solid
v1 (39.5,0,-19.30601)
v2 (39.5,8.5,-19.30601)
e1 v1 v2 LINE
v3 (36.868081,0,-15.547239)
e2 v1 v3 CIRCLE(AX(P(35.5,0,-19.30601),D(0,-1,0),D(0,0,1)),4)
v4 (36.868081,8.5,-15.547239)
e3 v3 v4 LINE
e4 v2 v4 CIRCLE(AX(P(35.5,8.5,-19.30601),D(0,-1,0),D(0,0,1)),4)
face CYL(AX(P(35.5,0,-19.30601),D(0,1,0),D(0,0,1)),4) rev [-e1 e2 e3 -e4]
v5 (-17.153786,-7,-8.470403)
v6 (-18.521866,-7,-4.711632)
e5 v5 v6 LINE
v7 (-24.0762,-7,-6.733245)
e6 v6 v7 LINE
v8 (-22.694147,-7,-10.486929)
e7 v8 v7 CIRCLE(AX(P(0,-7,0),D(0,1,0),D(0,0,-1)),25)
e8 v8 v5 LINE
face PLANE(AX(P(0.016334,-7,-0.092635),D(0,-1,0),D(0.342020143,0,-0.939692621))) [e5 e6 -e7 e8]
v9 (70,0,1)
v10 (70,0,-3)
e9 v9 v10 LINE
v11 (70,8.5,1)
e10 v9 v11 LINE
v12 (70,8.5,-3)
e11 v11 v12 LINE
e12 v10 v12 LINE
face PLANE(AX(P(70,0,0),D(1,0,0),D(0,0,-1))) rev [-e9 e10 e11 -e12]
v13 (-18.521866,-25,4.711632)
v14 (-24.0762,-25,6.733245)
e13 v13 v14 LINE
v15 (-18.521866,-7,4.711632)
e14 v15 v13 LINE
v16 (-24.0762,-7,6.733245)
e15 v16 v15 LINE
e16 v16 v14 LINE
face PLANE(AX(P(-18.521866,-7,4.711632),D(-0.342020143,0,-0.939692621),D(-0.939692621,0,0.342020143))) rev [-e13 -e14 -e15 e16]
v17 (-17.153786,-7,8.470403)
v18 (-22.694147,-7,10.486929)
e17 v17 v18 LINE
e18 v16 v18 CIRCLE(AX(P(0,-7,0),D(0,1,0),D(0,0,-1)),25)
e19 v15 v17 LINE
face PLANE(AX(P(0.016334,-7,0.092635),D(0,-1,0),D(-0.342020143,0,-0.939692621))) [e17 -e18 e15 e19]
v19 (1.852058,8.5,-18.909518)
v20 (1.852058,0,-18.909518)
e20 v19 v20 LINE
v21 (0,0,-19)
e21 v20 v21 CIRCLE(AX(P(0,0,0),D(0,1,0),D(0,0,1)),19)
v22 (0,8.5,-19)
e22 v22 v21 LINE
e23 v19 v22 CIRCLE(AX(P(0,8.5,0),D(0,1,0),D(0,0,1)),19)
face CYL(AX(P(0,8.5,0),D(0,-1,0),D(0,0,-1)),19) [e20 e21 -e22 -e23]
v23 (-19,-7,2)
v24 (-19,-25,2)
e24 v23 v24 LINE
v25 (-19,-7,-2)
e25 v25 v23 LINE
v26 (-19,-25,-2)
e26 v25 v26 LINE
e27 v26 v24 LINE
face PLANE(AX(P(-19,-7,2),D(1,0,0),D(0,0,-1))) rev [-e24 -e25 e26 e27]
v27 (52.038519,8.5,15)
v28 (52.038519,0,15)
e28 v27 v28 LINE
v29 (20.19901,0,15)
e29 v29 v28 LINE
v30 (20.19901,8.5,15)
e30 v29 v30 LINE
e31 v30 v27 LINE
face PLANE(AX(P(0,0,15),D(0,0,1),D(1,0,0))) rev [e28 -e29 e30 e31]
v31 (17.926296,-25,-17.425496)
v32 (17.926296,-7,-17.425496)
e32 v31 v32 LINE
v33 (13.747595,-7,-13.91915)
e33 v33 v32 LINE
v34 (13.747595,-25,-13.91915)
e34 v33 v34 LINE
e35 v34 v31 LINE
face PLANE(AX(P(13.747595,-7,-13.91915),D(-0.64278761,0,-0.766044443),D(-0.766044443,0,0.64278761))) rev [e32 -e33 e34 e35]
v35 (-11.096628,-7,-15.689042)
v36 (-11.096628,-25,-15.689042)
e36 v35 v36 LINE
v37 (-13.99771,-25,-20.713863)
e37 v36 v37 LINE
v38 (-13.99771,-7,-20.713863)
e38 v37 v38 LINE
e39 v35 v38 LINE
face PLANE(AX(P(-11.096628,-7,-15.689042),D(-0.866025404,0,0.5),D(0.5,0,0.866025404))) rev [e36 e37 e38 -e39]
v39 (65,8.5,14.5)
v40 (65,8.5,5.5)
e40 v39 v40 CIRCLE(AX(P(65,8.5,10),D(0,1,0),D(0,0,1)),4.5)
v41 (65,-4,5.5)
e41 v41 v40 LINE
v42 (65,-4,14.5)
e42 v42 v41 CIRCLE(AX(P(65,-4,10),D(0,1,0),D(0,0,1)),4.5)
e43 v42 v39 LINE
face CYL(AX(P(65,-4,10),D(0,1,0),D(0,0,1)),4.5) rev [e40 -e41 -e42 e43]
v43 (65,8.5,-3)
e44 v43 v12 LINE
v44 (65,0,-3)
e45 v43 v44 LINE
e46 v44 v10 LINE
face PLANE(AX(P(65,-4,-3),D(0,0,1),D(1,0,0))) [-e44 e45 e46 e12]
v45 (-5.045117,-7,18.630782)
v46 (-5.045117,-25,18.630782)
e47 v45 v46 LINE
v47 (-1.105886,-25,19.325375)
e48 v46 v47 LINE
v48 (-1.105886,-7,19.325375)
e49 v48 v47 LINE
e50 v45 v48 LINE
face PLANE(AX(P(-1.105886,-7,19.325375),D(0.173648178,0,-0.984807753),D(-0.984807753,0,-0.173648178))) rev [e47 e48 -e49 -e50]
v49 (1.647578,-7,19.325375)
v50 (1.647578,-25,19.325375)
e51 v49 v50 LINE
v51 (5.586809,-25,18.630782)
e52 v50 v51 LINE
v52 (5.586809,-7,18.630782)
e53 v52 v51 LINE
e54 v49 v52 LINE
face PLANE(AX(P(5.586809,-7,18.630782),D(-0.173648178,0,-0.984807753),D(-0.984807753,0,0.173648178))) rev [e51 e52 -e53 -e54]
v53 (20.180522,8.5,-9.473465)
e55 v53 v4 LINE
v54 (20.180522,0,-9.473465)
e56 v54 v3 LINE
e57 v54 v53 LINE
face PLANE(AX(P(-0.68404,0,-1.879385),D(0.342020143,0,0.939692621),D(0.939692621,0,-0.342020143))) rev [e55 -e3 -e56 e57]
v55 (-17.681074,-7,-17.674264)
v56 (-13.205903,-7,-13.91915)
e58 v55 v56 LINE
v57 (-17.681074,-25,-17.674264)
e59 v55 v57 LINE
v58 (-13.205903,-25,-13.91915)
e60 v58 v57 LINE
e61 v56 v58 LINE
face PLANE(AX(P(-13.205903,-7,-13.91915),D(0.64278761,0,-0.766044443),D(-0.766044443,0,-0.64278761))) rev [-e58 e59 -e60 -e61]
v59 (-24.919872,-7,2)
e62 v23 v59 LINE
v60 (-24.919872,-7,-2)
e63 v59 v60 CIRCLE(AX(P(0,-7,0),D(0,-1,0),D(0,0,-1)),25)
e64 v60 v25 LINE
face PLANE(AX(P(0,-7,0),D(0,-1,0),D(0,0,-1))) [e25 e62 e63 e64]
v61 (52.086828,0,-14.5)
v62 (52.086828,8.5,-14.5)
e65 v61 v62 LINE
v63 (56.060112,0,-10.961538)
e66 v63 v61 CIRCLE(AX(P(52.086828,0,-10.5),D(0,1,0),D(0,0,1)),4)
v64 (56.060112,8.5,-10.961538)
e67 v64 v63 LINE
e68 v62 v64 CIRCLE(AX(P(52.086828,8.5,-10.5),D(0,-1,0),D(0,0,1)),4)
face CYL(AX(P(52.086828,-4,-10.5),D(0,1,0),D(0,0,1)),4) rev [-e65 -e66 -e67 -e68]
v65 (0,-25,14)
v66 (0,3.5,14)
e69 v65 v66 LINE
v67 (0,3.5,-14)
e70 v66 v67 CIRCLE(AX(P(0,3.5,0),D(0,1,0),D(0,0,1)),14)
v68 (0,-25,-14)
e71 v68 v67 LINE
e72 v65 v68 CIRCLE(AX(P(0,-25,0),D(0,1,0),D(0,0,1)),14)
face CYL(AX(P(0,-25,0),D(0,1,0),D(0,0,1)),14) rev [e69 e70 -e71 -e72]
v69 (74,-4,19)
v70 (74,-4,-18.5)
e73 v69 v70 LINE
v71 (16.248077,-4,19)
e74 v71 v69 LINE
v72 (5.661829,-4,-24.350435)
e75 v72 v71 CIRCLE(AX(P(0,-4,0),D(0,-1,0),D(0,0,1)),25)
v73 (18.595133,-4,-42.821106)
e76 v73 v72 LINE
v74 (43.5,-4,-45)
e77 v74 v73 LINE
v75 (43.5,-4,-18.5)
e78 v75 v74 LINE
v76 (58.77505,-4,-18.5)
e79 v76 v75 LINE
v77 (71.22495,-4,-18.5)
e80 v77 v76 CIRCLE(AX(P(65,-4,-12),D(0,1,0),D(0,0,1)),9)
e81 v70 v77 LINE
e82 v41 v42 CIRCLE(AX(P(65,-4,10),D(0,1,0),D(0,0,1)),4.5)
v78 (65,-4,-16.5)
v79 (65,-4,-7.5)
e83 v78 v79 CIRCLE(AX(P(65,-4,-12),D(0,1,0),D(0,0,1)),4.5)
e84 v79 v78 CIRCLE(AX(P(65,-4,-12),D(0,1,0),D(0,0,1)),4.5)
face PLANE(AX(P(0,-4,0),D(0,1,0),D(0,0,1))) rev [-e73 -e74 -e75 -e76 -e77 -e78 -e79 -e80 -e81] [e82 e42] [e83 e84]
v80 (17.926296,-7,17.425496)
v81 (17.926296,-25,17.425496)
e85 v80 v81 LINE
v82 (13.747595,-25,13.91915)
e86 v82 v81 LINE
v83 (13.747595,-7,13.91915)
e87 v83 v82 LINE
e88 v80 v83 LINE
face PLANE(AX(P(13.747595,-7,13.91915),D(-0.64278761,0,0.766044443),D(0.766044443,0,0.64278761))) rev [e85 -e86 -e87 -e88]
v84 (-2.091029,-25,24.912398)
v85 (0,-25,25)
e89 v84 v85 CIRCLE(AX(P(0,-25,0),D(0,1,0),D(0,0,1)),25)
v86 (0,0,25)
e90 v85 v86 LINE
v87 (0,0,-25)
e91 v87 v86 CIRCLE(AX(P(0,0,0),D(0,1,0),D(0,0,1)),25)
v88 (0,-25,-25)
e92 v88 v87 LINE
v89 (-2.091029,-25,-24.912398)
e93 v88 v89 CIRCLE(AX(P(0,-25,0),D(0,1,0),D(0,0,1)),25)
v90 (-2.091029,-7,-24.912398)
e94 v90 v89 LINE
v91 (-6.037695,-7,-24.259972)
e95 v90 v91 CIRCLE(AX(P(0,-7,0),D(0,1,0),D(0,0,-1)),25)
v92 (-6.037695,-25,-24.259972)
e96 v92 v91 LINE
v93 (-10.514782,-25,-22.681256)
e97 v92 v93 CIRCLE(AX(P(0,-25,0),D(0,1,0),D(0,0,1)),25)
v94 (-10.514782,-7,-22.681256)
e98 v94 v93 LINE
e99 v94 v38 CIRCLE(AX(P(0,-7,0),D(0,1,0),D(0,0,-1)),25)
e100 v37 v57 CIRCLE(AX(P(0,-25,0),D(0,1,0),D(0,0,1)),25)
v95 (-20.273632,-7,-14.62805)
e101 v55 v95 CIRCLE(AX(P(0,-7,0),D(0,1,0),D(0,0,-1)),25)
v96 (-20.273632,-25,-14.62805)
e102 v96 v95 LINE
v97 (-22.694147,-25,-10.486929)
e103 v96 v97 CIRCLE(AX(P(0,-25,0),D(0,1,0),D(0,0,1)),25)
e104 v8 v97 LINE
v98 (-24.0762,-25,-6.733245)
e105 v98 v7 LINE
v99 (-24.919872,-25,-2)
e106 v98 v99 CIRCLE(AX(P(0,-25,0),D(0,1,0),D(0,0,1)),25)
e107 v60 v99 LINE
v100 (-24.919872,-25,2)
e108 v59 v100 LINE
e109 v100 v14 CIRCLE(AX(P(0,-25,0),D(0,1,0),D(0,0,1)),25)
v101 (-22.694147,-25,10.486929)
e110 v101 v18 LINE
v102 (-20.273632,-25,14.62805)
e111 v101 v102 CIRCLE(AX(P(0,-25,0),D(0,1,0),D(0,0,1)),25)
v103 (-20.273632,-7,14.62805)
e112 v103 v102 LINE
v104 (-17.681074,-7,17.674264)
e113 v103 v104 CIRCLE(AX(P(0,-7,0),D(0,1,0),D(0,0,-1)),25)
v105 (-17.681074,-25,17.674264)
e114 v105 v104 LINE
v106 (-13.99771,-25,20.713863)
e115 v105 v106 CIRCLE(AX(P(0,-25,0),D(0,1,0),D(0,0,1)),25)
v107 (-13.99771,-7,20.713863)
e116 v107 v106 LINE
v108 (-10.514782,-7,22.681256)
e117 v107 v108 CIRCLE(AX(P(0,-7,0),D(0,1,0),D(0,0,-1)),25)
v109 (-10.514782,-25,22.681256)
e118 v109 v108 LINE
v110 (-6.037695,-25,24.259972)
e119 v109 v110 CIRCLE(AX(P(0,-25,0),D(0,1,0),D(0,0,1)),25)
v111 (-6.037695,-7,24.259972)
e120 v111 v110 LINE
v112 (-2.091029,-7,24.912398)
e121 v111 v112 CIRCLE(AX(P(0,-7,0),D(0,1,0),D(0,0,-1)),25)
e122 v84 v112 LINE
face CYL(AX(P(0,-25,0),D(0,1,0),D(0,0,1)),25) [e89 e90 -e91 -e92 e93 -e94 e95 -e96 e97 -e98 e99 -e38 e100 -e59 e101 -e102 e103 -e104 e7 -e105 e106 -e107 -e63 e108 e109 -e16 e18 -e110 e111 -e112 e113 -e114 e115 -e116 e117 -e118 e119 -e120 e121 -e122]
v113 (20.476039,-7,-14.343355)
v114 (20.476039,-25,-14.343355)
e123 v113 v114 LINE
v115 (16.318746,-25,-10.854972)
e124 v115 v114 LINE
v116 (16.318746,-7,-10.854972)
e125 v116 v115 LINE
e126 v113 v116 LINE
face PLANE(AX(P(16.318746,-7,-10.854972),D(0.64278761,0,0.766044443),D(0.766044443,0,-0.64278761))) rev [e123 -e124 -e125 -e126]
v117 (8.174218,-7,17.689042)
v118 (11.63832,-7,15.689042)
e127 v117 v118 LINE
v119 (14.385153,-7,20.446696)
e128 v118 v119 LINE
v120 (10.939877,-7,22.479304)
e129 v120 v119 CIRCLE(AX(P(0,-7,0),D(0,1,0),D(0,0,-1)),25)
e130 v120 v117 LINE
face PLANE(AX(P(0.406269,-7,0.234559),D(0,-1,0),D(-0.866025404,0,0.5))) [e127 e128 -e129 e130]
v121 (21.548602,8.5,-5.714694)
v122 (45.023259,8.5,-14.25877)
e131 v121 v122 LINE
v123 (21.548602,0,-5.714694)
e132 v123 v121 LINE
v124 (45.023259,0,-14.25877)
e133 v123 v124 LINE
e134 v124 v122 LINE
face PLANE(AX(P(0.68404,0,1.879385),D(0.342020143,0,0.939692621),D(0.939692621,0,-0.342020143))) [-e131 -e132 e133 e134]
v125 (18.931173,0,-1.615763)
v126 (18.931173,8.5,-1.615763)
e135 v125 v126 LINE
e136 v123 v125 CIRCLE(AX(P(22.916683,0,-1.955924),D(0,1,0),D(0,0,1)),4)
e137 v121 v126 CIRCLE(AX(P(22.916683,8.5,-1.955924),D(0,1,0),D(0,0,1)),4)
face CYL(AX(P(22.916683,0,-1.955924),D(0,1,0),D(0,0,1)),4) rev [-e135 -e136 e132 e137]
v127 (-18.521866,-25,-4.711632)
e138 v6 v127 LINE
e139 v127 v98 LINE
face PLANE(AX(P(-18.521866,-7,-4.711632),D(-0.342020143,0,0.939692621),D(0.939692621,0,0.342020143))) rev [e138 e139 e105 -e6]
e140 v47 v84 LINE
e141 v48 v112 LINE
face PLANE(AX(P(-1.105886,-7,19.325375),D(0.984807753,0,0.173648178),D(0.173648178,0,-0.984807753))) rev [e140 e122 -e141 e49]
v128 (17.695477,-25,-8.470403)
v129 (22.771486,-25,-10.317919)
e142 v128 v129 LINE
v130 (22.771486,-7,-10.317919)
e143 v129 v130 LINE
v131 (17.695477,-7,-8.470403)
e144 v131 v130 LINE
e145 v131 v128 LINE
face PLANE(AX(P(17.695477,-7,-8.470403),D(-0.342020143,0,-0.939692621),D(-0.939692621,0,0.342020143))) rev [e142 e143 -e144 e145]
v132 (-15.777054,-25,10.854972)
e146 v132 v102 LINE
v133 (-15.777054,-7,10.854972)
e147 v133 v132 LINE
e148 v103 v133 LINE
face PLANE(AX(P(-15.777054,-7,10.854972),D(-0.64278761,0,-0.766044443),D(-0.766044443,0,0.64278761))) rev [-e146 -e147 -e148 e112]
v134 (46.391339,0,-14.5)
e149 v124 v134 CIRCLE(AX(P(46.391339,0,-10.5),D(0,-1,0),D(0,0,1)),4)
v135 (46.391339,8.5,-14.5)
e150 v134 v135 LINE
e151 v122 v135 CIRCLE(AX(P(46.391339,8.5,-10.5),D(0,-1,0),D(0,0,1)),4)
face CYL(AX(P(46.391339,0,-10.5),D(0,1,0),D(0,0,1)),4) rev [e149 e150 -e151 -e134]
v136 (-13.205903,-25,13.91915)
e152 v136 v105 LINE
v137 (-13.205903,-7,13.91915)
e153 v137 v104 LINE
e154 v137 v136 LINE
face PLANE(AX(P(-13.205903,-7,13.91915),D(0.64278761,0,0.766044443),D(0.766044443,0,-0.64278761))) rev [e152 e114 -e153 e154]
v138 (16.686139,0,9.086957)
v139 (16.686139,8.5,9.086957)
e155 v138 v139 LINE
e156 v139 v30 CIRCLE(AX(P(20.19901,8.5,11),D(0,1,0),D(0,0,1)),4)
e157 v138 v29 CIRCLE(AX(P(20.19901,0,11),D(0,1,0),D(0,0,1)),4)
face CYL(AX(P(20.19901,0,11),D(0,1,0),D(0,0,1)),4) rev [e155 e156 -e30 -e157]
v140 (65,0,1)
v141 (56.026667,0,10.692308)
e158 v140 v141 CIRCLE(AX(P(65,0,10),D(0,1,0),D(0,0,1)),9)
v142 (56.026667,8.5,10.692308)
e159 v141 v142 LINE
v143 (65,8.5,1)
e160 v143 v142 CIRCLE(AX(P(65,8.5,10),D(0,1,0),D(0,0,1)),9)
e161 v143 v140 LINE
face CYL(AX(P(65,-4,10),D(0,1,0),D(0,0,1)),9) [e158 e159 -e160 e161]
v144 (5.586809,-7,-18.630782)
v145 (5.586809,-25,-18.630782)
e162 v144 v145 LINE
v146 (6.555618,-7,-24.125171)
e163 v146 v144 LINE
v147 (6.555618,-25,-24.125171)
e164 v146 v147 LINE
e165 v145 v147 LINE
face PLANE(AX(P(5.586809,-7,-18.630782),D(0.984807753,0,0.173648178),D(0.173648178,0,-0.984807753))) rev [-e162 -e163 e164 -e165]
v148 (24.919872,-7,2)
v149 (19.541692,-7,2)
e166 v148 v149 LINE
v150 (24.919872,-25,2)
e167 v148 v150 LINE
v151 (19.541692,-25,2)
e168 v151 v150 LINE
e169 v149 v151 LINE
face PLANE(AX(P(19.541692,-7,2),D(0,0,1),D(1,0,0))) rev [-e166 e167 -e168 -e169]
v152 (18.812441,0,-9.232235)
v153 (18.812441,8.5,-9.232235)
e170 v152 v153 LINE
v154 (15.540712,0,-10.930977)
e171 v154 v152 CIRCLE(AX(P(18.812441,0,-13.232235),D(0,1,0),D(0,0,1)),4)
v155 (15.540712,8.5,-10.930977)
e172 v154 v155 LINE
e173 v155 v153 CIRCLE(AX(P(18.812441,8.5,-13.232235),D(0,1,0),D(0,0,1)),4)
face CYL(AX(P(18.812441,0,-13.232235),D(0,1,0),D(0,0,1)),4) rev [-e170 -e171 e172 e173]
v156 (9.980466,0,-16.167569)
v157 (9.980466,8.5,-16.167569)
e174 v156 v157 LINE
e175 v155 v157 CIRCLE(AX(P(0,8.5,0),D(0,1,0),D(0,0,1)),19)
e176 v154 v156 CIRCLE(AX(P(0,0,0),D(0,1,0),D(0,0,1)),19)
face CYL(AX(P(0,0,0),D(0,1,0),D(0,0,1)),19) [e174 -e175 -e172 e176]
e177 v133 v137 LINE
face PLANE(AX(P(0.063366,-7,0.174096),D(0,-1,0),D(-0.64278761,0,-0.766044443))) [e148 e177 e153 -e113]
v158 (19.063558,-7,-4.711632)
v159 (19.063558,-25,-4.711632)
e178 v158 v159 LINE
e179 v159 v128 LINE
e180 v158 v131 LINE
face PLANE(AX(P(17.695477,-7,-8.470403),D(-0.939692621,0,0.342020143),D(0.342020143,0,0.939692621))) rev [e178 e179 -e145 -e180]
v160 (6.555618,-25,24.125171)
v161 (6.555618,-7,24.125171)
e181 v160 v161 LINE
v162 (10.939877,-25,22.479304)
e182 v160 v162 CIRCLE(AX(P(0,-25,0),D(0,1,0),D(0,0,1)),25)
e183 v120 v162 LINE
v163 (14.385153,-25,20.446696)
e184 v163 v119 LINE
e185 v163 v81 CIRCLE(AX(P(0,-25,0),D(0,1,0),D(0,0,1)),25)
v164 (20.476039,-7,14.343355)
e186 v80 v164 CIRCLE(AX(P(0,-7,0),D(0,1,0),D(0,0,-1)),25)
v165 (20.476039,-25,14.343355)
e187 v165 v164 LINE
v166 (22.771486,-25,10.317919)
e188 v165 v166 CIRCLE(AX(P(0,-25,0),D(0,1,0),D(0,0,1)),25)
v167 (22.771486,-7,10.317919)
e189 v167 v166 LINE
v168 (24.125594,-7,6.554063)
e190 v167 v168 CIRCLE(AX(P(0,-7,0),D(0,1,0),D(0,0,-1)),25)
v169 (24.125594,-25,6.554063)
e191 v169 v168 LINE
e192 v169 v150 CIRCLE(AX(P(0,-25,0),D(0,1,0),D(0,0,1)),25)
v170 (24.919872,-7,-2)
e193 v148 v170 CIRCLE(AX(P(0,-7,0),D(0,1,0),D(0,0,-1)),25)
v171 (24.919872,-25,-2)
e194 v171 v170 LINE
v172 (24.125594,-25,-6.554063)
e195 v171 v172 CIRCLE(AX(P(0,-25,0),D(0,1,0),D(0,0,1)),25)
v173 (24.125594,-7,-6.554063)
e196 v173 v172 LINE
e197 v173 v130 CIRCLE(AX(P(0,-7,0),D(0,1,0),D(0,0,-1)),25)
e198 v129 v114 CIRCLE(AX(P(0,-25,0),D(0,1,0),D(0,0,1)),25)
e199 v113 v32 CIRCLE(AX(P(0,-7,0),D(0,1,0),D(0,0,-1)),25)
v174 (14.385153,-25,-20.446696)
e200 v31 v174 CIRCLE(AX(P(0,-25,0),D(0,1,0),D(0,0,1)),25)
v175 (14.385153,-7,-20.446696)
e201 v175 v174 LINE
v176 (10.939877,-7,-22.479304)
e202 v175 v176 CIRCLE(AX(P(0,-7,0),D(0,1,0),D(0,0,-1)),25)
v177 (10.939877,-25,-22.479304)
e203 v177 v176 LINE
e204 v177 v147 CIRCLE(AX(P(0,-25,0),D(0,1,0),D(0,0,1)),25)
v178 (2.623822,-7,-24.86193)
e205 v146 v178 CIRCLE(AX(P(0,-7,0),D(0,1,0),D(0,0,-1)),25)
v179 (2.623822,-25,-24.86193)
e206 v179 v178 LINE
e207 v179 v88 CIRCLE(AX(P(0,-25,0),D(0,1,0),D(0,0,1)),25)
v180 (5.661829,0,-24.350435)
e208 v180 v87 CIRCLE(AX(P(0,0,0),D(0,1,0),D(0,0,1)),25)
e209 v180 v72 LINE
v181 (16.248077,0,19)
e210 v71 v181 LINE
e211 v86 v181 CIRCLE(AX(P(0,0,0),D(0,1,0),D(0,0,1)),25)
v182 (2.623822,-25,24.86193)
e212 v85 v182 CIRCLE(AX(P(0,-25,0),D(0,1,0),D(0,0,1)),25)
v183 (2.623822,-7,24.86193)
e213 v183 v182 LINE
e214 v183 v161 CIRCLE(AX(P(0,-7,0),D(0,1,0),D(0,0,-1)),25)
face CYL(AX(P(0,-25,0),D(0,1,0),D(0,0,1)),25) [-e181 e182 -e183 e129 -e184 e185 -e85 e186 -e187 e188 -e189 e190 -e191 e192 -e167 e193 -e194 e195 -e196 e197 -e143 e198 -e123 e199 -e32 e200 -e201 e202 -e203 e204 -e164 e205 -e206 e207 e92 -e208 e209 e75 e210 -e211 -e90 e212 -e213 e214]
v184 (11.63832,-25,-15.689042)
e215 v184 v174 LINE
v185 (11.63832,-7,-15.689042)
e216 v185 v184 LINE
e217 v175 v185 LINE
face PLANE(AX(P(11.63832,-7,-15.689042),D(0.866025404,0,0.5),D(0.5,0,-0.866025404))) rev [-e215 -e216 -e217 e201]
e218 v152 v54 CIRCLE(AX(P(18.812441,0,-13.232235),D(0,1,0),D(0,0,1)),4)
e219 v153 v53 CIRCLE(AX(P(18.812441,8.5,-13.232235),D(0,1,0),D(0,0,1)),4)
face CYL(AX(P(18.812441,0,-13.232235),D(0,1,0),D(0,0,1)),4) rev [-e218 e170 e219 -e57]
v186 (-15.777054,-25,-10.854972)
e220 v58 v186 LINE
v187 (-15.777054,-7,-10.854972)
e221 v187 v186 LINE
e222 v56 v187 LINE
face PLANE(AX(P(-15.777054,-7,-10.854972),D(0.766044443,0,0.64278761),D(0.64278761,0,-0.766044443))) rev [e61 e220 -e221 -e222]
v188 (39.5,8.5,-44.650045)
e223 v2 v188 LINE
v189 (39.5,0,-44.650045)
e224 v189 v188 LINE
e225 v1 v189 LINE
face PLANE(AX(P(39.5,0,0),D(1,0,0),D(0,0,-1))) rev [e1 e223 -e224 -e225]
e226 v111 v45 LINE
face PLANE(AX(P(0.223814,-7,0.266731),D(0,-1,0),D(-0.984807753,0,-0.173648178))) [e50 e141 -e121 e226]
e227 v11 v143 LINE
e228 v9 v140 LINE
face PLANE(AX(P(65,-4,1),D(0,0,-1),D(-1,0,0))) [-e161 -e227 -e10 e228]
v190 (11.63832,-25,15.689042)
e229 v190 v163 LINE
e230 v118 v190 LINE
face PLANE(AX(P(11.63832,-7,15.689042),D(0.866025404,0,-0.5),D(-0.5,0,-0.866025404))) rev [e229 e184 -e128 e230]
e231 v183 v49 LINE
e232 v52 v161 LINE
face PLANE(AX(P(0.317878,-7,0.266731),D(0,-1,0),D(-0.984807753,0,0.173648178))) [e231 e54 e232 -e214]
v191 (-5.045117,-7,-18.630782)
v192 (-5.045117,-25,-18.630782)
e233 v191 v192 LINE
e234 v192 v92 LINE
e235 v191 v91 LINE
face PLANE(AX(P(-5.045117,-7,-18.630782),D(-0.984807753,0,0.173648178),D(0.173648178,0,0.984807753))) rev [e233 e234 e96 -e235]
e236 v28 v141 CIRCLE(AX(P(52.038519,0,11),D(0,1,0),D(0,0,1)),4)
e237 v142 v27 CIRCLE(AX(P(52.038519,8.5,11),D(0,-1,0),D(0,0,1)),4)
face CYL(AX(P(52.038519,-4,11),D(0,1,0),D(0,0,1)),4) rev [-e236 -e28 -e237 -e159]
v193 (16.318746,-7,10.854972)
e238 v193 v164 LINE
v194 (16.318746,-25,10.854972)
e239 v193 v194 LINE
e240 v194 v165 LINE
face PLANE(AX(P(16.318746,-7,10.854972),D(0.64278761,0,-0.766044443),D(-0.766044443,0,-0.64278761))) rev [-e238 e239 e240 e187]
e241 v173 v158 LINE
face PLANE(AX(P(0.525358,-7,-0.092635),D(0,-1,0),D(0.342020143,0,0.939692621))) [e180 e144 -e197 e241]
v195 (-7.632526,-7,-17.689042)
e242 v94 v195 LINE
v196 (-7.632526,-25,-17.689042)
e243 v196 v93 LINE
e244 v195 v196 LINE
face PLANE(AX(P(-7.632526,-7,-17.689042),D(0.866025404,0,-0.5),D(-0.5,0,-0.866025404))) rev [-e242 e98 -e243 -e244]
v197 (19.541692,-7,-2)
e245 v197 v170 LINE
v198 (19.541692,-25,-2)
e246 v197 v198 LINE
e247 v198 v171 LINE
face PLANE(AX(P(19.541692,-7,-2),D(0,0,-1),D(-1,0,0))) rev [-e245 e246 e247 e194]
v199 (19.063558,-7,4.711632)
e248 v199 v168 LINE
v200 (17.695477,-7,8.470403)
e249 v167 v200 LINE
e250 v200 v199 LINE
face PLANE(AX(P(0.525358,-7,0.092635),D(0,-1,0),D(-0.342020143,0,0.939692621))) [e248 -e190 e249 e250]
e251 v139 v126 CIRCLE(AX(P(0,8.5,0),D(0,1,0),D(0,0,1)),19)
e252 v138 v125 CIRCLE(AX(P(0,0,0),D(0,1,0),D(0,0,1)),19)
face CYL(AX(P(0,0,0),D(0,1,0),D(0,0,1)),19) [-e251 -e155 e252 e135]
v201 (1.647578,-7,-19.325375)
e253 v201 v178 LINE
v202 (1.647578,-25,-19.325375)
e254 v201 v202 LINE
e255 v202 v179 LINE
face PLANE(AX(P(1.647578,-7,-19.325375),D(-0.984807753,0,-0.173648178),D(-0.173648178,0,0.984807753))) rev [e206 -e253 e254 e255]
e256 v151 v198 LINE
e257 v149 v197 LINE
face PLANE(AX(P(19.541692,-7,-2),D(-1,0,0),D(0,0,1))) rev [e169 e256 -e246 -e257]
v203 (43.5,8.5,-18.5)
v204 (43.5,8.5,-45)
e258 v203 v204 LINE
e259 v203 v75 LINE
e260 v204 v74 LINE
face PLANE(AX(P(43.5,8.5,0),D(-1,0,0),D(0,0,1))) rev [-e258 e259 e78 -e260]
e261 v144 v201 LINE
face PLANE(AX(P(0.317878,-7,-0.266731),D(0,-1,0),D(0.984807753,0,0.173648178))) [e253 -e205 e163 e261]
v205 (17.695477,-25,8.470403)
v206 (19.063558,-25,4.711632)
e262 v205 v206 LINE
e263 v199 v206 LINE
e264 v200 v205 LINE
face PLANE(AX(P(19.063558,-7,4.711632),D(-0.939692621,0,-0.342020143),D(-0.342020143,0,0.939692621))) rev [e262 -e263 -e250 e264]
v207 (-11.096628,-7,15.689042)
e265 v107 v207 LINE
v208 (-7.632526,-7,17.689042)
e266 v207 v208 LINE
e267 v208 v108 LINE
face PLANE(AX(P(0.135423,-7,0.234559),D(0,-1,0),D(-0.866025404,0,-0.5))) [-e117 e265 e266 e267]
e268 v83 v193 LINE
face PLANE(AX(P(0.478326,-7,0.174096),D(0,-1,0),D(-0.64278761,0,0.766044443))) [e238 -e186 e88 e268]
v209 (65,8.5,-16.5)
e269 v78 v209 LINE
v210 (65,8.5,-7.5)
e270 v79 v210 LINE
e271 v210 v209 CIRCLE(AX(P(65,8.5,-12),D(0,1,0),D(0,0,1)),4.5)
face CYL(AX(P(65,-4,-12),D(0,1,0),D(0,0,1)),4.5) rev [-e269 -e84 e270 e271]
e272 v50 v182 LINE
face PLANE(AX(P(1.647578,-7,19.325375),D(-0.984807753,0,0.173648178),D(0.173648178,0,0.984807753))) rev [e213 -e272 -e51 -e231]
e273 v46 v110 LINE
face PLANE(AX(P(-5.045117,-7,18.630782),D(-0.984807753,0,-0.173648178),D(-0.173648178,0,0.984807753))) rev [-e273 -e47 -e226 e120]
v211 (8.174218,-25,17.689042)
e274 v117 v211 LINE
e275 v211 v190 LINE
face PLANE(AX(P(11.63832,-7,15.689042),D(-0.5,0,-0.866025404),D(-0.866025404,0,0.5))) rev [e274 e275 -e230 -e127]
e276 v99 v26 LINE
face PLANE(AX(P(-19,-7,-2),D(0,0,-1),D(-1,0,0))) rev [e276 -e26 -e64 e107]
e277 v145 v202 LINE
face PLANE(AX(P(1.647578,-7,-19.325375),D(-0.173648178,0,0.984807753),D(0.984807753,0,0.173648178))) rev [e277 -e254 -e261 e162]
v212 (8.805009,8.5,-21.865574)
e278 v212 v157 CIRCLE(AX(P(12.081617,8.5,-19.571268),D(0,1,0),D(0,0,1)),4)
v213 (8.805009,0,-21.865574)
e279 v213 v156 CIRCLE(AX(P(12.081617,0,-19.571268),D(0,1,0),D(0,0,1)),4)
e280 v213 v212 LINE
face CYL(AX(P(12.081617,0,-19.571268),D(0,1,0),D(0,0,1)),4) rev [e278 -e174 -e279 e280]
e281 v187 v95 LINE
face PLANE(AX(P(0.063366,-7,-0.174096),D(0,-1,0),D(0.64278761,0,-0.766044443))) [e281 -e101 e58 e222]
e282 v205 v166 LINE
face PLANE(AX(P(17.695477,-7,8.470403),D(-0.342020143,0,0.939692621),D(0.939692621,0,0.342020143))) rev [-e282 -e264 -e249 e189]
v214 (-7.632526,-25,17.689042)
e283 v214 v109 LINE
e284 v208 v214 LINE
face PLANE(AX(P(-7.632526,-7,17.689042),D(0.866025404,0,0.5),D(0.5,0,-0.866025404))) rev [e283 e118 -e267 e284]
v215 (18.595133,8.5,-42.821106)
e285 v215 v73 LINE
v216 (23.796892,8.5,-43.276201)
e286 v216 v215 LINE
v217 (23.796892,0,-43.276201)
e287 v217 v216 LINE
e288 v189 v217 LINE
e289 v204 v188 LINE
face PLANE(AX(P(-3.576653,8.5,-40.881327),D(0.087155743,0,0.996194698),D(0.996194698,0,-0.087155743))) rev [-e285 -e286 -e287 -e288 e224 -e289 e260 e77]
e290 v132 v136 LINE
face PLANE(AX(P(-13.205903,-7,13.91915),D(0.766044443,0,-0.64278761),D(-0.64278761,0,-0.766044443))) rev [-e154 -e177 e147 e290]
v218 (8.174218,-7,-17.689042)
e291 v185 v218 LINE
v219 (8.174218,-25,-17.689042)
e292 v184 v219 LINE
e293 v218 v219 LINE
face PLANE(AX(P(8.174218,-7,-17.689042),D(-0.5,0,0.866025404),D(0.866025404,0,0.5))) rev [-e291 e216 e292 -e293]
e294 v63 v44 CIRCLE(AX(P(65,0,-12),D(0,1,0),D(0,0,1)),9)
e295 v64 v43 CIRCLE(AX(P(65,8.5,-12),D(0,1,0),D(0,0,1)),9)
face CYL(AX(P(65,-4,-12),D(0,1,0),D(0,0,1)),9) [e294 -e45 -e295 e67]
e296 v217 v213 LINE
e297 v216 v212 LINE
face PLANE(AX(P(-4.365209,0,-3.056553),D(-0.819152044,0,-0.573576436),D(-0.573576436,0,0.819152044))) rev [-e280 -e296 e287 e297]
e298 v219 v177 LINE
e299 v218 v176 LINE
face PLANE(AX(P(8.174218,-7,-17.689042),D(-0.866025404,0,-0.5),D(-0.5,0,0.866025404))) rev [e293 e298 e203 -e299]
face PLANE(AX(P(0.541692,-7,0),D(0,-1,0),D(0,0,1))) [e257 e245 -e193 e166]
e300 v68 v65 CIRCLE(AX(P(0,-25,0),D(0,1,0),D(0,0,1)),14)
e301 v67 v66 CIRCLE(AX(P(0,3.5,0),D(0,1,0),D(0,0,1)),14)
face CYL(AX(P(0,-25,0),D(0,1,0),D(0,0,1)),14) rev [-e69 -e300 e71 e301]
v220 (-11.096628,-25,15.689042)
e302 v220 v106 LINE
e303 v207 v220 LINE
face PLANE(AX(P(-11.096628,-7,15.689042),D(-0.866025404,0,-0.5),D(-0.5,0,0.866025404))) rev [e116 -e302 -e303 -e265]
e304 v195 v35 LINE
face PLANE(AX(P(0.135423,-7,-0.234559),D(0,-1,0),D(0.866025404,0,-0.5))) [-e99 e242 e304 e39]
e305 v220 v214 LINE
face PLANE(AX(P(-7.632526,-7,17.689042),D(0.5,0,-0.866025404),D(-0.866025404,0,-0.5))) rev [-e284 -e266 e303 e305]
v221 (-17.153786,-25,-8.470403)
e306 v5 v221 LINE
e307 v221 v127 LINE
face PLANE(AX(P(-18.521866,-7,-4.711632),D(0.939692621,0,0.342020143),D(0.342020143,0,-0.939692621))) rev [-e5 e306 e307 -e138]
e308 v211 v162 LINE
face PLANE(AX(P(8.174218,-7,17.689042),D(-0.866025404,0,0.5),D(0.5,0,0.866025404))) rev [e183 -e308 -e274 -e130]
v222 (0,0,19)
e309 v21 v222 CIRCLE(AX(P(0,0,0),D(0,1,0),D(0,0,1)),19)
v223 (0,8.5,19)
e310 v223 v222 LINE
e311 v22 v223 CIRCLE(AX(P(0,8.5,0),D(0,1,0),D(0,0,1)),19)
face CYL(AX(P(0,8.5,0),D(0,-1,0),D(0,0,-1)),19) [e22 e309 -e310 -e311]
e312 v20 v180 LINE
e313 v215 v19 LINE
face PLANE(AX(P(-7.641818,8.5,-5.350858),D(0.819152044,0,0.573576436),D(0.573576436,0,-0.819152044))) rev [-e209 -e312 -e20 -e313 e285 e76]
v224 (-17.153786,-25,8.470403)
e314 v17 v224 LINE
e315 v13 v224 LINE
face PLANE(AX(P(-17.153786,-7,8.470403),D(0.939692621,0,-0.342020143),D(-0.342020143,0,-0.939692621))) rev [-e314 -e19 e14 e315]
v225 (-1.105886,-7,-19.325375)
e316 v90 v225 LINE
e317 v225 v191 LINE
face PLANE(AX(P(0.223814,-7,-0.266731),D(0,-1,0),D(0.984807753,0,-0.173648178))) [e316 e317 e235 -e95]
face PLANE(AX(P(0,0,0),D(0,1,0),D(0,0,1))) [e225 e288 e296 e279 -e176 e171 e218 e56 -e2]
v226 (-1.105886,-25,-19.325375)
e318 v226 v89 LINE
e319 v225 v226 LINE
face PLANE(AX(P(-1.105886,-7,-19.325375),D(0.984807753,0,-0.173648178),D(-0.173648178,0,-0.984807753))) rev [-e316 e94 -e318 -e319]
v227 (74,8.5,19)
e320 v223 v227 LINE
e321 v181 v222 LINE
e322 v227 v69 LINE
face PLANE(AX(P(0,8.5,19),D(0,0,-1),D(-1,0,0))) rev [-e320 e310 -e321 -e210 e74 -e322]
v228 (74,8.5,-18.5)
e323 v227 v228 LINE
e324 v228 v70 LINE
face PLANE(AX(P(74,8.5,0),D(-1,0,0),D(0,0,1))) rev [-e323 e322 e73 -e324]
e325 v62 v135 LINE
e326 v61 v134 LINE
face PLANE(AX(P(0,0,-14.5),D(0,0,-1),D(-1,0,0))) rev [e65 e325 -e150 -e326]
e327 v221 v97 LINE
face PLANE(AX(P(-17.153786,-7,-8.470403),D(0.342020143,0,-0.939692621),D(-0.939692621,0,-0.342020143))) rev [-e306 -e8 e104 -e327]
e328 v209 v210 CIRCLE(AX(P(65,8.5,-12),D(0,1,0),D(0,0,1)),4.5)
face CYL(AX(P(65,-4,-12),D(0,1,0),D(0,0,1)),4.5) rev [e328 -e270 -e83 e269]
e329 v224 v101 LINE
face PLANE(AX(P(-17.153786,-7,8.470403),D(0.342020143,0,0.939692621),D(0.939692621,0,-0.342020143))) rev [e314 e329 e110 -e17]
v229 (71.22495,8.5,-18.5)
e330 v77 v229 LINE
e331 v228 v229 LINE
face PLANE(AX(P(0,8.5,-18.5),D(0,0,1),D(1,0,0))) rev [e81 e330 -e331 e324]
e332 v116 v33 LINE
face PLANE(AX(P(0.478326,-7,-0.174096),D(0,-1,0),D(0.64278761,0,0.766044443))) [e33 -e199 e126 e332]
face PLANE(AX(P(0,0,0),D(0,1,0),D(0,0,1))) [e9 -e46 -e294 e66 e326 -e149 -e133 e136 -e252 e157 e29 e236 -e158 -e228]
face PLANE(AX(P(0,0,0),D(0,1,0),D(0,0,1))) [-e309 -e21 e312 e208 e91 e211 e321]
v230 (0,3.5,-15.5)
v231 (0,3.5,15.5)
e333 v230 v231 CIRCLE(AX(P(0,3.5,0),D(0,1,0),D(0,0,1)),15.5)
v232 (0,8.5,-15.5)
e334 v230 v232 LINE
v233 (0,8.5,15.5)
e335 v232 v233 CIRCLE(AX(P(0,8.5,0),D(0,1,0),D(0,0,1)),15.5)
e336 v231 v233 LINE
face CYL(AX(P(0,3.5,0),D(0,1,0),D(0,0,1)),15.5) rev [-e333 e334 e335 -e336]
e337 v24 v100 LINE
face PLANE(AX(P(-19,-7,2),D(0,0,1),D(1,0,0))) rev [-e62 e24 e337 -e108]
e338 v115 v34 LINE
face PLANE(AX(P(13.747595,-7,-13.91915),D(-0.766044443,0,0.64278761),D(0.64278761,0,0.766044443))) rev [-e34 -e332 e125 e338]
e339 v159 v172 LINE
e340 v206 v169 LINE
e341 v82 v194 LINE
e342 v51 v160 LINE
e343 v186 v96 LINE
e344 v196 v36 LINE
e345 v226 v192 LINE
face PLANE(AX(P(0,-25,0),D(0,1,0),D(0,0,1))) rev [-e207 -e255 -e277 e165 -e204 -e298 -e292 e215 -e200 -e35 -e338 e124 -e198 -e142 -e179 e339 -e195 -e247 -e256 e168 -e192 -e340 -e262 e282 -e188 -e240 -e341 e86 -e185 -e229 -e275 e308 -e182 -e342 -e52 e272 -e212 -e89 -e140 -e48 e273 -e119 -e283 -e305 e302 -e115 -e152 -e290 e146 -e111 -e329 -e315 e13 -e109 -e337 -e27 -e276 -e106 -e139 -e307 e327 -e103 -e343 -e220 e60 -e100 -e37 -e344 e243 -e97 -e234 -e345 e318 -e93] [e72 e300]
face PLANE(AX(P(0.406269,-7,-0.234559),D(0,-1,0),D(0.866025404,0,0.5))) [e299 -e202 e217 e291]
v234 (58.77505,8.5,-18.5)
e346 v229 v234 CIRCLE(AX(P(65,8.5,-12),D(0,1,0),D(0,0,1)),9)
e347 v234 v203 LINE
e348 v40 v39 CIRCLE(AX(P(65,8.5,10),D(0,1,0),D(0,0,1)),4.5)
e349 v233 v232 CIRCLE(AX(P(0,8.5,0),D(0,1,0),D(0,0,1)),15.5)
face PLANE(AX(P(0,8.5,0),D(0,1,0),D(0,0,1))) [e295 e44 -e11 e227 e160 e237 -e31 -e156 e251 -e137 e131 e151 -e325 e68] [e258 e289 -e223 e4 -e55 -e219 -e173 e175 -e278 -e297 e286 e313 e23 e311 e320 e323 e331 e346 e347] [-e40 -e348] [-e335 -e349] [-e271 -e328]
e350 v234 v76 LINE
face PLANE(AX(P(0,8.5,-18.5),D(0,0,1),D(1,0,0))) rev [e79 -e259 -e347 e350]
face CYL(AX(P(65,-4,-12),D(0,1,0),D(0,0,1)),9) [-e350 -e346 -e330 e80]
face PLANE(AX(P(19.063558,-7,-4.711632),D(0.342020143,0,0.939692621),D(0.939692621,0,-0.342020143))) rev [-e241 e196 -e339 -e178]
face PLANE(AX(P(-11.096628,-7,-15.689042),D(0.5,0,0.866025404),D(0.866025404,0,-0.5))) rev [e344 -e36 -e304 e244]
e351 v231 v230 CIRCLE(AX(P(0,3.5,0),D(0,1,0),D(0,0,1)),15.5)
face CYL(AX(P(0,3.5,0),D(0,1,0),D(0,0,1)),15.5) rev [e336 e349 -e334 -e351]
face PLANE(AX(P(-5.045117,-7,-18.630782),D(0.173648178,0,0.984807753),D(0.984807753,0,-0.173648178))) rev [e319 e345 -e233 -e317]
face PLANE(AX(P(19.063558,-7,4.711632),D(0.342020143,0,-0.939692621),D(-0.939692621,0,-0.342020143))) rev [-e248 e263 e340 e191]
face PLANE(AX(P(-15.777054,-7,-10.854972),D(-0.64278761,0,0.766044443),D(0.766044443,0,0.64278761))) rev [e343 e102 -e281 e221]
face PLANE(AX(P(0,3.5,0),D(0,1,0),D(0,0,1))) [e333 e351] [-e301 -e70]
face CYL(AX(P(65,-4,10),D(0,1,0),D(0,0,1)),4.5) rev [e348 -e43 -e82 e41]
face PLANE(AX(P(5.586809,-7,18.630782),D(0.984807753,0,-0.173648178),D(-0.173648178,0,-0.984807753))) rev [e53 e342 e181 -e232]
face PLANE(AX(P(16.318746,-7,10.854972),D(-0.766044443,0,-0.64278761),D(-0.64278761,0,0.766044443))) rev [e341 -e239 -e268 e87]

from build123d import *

# Parameters (mm, degrees)
HUB_PROFILE_50_R             = 25
HUB_50_DEPTH                 = 25
SERRATION_START              = -18
SERRATION_SLOT_DEPTH         = 18
SERRATION_PATTERN_18X_COUNT  = 18
ARM_OUTLINE_PROFILE_R        = 19
ARM_PLATE_DEPTH              = 8.5
ARM_START                    = -4
ARM_RIM_WALL_DEPTH           = 12.5
ARM_START_2                  = -8.5
ARM_POCKET_DEPTH             = 8.5
ARM_END_BOSS_PROFILE_R       = 9
ARM_END_BOSSES_DEPTH         = 12.5
ARM_END_HOLE_PROFILE_9_R     = 4.5
ARM_END_HOLES_9_DEPTH        = 12.5
HUB_COUNTERBORE_PROFILE_31_R = 15.5
HUB_COUNTERBORE_31_DEPTH     = 5
HUB_BORE_PROFILE_28_R        = 14
HUB_BORE_28_DEPTH            = 92.177025615
POCKET_FILLET_R4_R           = 4
SIDE_WALL_DEPTH              = 12.5


with BuildPart() as part:
    # Hub Profile _50 → Hub _50 (new body)
    with BuildSketch(Plane(origin=(0, 0, 0), x_dir=(1, 0, 0), z_dir=(0, 1, 0))):
        with Locations(Location((0, 0, 0), (0, 0, 270))):
            Circle(HUB_PROFILE_50_R)
    extrude(amount=-HUB_50_DEPTH)

    # Serration Slot Profile → Serration Slot (cut)
    with BuildSketch(Plane.XZ.offset(25).offset(SERRATION_START)):
        with BuildLine():
            Line((-19, 2), (-24.919871589, 2))
            ThreePointArc((-24.919871589, 2), (-25, 0), (-24.919871589, -2))
            Line((-24.919871589, -2), (-19, -2))
            Line((-19, -2), (-19, 2))
        make_face()
    serration_slot = extrude(amount=SERRATION_SLOT_DEPTH, mode=Mode.SUBTRACT)

    # Serration Pattern 18x: Serration Slot ×18 about axis
    serration_pattern_18x_axis = Axis((0.270845918, 0, 0), (0, 1, 0))
    for i in range(1, SERRATION_PATTERN_18X_COUNT):
        add(serration_slot.rotate(serration_pattern_18x_axis, i * 360 / SERRATION_PATTERN_18X_COUNT), mode=Mode.SUBTRACT)

    # Arm Outline Profile → Arm Plate (add)
    with BuildSketch(Plane(origin=(0, 0, 0), x_dir=(1, 0, 0), z_dir=(0, 1, 0))):
        with Locations(Location((0, 0, 0), (0, 0, 270))):
            Circle(ARM_OUTLINE_PROFILE_R)
    extrude(amount=ARM_PLATE_DEPTH)

    # Sketch3_5 → Arm Rim Wall (add)
    with BuildSketch(Plane(origin=(0, 0, 0), x_dir=(1, 0, 0), z_dir=(0, 1, 0)).offset(ARM_START)):
        with BuildLine():
            ThreePointArc((19, 0), (13.435028843, -13.435028843), (0, -19))
            Line((0, -19), (74, -19))
            Line((74, -19), (74, 18.5))
            Line((74, 18.5), (43.5, 18.5))
            Line((43.5, 18.5), (43.5, 45))
            Line((43.5, 45), (18.595132548, 42.821106431))
            Line((18.595132548, 42.821106431), (1.852058249, 18.909518245))
            ThreePointArc((1.852058249, 18.909518245), (14.074606686, 12.763441802), (19, 0))
        make_face()
    extrude(amount=ARM_RIM_WALL_DEPTH)

    # Arm Pocket Profile → Arm Pocket (cut)
    with BuildSketch(Plane(origin=(0, 8.5, 0), x_dir=(1, 0, 0), z_dir=(0, 1, 0)).offset(ARM_START_2)):
        with BuildLine():
            ThreePointArc((45.023258732, 14.258770483), (45.696746595, 14.439231012), (46.391339305, 14.5))
            Line((46.391339305, 14.5), (70, 14.5))
            Line((70, 14.5), (70, -15))
            Line((70, -15), (20.199009877, -15))
            ThreePointArc((20.199009877, -15), (16.760102062, -13.043015674), (16.686138594, -9.086956522))
            ThreePointArc((16.686138594, -9.086956522), (18.595302437, -3.900606013), (18.931172951, 1.61576319))
            ThreePointArc((18.931172951, 1.61576319), (19.545401033, 4.1087029), (21.548602473, 5.714694345))
            Line((21.548602473, 5.714694345), (45.023258732, 14.258770483))
        make_face()
        with BuildLine():
            Line((23.79689183, 43.276201399), (21.871740725, 40.526800686))
            Line((21.871740725, 40.526800686), (8.805008905, 21.865573683))
            ThreePointArc((8.805008905, 21.865573683), (8.164106806, 18.763113723), (9.980466285, 16.167569166))
            ThreePointArc((9.980466285, 16.167569166), (13.026439067, 13.831553971), (15.5407124, 10.930976996))
            ThreePointArc((15.5407124, 10.930976996), (17.613669166, 9.416092585), (20.1805219, 9.473464828))
            Line((20.1805219, 9.473464828), (36.868080573, 15.547239468))
            ThreePointArc((36.868080573, 15.547239468), (38.776608177, 17.011704206), (39.5, 19.306009951))
            Line((39.5, 19.306009951), (39.5, 44.650045346))
            Line((39.5, 44.650045346), (23.79689183, 43.276201399))
        make_face()
    extrude(amount=ARM_POCKET_DEPTH, mode=Mode.SUBTRACT)

    # Arm End Boss Profile → Arm End Bosses (add)
    with BuildSketch(Plane(origin=(0, 8.5, 0), x_dir=(1, 0, 0), z_dir=(0, 1, 0))):
        with Locations((65, 12)):
            Circle(ARM_END_BOSS_PROFILE_R)
        with Locations((65, -10)):
            Circle(ARM_END_BOSS_PROFILE_R)
    extrude(amount=-ARM_END_BOSSES_DEPTH)

    # Arm End Hole Profile _9 → Arm End Holes _9 (cut)
    with BuildSketch(Plane(origin=(0, 8.5, 0), x_dir=(1, 0, 0), z_dir=(0, 1, 0))):
        with Locations(Location((65, 12, 0), (0, 0, 270))):
            Circle(ARM_END_HOLE_PROFILE_9_R)
        with Locations(Location((65, -10, 0), (0, 0, 270))):
            Circle(ARM_END_HOLE_PROFILE_9_R)
    extrude(amount=-ARM_END_HOLES_9_DEPTH, mode=Mode.SUBTRACT)

    # Hub Counterbore Profile _31 → Hub Counterbore _31 (cut)
    with BuildSketch(Plane(origin=(0, 8.5, 0), x_dir=(1, 0, 0), z_dir=(0, 1, 0))):
        with Locations(Location((0, 0, 0), (0, 0, 270))):
            Circle(HUB_COUNTERBORE_PROFILE_31_R)
    extrude(amount=-HUB_COUNTERBORE_31_DEPTH, mode=Mode.SUBTRACT)

    # Hub Bore Profile _28 → Hub Bore _28 (cut, through all)
    with BuildSketch(Plane(origin=(0, 3.5, 0), x_dir=(1, 0, 0), z_dir=(0, 1, 0))):
        with Locations(Location((0, 0, 0), (0, 0, 270))):
            Circle(HUB_BORE_PROFILE_28_R)
    extrude(amount=-HUB_BORE_28_DEPTH, mode=Mode.SUBTRACT)

    # Pocket Fillet R4
    pocket_fillet_r4_edges = [part.edges().sort_by_distance(p)[0] for p in [
        (56.354191767, 4.25, -14.5),
        (57.516685226, 4.25, 15),
    ]]
    fillet(pocket_fillet_r4_edges, radius=POCKET_FILLET_R4_R)

    # Side Wall Profile → Side Wall (add)
    with BuildSketch(Plane(origin=(0, 8.5, 0), x_dir=(1, 0, 0), z_dir=(0, 1, 0))):
        with BuildLine():
            Line((65, 3), (70, 3))
            Line((70, 3), (70, 4.516685226))
            ThreePointArc((70, 4.516685226), (67.61248608, 3.38751392), (65, 3))
        make_face()
        with BuildLine():
            Line((65, -1), (70, -1))
            Line((70, -1), (70, -2.516685226))
            ThreePointArc((70, -2.516685226), (67.61248608, -1.38751392), (65, -1))
        make_face()
    extrude(amount=-SIDE_WALL_DEPTH)


solid = part.part
